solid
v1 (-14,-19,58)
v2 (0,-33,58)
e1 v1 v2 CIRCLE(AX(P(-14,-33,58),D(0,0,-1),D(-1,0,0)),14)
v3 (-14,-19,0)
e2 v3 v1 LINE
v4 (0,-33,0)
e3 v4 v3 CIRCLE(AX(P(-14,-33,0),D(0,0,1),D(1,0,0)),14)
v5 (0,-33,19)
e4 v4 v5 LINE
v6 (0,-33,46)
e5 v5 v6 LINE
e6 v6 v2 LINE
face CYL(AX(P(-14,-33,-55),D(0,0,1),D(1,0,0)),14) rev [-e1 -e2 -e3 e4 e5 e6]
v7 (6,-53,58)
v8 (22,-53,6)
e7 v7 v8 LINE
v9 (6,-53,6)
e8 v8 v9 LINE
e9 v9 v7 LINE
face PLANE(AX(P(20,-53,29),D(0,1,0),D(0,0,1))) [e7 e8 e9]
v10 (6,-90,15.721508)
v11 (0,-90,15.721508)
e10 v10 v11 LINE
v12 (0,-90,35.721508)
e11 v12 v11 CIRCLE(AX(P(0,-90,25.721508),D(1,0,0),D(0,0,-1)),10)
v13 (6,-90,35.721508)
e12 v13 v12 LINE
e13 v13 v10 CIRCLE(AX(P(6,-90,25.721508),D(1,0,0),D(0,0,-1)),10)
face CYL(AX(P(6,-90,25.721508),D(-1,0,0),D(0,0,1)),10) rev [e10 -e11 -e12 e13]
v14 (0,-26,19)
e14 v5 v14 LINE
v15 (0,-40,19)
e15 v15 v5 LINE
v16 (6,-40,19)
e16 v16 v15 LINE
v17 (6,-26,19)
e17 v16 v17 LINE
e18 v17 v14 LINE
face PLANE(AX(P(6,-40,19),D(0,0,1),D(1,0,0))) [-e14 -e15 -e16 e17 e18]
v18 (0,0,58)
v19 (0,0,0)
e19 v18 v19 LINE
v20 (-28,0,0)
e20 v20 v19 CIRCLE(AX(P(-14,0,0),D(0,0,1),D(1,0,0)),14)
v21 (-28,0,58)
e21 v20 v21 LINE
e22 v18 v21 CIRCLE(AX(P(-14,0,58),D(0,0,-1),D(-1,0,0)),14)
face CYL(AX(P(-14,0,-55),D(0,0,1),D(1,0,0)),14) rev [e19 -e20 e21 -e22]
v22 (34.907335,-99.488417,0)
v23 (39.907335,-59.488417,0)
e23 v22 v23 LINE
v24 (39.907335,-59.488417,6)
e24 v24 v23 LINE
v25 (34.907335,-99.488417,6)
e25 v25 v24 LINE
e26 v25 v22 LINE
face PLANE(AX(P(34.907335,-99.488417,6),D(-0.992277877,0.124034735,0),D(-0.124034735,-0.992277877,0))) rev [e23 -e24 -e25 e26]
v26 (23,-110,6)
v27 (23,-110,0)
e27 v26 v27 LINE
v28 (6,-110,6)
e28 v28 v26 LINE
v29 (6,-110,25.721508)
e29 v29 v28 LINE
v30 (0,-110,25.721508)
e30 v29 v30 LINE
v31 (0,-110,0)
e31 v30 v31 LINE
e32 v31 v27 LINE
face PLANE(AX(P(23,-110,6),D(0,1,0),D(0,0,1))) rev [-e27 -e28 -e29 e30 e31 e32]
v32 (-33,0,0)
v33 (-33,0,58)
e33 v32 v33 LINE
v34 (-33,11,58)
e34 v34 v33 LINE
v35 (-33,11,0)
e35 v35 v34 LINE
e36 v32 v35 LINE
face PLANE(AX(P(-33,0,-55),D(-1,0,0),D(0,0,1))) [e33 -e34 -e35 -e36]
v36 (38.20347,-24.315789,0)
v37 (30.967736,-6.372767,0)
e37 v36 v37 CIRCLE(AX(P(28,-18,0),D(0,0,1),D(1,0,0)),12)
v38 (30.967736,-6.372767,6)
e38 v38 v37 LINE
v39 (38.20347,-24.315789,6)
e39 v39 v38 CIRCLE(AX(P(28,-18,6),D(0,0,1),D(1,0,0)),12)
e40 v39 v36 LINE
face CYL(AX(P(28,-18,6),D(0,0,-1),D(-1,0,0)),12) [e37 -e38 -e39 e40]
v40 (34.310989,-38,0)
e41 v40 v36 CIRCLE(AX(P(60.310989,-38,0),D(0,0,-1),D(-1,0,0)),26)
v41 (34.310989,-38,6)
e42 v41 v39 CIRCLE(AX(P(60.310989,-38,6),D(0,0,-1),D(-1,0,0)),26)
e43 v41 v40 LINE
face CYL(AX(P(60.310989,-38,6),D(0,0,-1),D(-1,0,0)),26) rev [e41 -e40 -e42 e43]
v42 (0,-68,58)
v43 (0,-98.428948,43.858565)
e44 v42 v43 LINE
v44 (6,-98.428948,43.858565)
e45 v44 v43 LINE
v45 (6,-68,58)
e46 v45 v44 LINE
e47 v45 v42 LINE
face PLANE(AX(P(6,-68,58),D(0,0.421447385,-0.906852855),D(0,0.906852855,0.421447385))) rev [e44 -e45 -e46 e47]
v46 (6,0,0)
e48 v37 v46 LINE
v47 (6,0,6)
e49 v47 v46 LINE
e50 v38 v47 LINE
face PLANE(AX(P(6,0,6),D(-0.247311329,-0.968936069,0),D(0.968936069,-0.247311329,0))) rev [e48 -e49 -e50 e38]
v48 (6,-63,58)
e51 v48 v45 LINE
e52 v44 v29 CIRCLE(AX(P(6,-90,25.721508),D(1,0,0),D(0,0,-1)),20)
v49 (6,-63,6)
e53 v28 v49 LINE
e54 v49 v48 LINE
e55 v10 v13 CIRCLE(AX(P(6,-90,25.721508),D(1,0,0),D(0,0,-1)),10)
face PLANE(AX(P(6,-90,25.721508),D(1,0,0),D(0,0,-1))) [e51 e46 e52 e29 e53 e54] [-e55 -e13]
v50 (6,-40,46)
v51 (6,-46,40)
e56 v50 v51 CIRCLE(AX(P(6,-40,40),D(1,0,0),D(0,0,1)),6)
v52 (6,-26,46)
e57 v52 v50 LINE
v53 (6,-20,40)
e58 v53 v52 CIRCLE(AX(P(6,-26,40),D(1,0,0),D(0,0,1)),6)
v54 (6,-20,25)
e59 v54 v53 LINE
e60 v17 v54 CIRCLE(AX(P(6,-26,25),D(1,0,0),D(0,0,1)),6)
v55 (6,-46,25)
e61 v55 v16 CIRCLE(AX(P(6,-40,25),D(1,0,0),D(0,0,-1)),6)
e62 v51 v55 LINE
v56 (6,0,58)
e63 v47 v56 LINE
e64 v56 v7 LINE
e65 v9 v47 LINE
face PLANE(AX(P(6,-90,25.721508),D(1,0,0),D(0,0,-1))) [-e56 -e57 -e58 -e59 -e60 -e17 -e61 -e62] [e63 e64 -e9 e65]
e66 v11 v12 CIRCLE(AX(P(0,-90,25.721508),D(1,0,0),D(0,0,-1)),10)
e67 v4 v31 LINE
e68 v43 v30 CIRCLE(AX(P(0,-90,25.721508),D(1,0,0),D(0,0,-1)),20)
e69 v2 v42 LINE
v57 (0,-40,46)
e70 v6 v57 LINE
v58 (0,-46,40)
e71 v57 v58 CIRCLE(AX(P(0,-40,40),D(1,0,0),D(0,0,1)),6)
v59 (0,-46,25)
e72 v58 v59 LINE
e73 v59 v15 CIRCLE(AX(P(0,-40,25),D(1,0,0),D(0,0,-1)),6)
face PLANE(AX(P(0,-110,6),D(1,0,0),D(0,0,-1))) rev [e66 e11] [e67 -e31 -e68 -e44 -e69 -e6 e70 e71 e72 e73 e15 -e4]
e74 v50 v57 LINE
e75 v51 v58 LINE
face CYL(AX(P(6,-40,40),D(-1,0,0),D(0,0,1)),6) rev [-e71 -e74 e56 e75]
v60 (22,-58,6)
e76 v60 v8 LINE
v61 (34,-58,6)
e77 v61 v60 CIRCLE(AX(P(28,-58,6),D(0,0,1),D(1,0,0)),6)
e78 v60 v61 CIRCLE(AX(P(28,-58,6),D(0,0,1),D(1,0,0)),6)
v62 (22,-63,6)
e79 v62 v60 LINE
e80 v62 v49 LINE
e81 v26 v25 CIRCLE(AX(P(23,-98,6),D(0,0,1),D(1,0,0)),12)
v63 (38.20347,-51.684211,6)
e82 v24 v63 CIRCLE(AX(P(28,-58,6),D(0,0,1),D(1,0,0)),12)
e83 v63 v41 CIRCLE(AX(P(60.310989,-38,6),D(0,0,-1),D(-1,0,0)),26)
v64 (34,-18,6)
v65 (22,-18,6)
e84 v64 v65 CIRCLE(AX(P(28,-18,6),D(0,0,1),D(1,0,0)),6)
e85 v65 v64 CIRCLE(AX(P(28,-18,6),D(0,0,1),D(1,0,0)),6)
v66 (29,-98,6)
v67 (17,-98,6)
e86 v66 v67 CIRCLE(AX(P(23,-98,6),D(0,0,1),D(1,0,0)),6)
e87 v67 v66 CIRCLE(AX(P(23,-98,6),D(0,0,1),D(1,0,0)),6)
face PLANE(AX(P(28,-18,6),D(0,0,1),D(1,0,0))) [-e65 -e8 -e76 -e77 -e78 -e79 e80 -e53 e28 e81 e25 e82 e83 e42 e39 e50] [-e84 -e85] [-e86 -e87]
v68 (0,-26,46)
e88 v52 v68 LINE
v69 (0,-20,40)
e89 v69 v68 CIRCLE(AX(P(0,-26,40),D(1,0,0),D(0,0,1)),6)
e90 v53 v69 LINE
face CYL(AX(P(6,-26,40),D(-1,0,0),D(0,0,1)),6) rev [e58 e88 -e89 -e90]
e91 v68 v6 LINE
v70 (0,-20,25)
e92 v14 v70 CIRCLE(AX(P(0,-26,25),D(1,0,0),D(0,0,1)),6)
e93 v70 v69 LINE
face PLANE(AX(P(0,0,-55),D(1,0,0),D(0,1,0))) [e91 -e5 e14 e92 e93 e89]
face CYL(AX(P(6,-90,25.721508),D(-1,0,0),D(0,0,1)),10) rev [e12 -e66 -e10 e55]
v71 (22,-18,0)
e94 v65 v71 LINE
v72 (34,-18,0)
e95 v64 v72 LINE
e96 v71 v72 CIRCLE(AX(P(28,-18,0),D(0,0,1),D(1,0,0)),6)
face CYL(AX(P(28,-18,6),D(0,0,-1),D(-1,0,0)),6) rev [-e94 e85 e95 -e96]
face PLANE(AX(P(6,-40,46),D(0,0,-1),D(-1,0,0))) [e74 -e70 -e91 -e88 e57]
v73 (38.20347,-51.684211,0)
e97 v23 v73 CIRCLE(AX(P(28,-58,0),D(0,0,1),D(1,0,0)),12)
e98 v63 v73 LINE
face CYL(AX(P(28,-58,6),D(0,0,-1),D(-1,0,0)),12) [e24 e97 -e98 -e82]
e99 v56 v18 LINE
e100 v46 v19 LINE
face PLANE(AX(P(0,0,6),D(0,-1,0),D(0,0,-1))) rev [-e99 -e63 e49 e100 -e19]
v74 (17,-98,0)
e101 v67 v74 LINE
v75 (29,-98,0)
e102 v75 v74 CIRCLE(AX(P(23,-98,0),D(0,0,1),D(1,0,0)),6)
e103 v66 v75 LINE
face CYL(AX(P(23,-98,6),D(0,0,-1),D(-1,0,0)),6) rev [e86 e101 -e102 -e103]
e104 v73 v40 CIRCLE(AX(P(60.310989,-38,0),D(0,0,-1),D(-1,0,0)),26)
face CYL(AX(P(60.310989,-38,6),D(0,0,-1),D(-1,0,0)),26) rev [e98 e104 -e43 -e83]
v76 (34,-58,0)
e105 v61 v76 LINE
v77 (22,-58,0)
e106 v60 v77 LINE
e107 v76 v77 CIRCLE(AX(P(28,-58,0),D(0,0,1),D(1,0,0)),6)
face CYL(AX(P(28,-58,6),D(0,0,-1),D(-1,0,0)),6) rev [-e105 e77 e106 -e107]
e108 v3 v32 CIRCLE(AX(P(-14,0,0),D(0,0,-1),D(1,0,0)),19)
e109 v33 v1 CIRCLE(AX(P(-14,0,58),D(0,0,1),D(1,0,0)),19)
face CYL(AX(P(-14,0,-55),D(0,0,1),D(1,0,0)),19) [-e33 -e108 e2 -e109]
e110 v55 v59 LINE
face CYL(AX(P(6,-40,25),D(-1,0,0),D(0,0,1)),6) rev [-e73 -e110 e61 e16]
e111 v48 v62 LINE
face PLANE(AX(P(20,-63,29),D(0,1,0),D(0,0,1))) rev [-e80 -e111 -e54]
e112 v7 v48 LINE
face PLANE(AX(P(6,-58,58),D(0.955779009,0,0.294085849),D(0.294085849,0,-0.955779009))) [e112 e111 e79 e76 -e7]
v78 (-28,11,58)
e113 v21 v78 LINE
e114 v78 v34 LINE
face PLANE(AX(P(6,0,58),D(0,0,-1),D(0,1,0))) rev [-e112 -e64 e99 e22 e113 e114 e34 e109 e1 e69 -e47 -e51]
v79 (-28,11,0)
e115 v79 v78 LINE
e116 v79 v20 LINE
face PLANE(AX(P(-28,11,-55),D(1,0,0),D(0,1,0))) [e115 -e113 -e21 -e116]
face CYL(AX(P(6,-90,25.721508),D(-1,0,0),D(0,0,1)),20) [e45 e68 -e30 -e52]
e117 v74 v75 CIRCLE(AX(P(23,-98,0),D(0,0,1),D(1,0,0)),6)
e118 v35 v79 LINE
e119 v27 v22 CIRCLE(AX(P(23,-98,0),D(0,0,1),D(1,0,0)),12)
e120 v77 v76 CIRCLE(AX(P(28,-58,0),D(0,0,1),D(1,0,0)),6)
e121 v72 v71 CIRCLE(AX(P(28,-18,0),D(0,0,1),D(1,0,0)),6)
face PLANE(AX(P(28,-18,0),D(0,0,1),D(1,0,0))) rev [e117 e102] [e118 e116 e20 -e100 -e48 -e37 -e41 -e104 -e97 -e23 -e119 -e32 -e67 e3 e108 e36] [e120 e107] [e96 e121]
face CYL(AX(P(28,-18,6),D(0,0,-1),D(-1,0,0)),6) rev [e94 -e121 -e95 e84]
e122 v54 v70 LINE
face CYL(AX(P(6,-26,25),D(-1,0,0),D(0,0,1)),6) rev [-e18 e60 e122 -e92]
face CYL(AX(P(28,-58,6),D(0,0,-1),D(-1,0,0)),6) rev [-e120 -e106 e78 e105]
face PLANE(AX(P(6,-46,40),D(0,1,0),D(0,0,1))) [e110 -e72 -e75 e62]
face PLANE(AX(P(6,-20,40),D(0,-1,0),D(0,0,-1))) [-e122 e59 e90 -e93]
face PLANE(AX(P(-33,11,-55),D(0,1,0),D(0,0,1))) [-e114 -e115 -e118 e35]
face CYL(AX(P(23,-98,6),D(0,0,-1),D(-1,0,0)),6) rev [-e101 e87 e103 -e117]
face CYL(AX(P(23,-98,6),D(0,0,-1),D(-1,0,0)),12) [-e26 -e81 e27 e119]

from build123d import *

# Parameters (mm, degrees)
BACK_PLATE_PROFILE_R   = 6
BACK_PLATE_6MM_DEPTH   = 6
SIDE_FLANGE_PROFILE_R  = 10
SIDE_FLANGE_6MM_DEPTH  = 6
GUSSET_RIB_10MM_REACH  = 93.258
GUSSET_RIB_PATH_WALL_W = 238.92163478
GUSSET_RIB_PATH_WALL_H = 10
CRADLE_SADDLE_REACH    = 132.629


with BuildPart() as part:
    # Back Plate Profile → Back Plate 6mm (new body)
    with BuildSketch(Plane.XY):
        with BuildLine():
            Line((0, 0), (6, 0))
            Line((6, 0), (30.967735953, -6.372767169))
            ThreePointArc((30.967735953, -6.372767169), (39.129158997, -13.512036094), (38.203470161, -24.315789474))
            ThreePointArc((38.203470161, -24.315789474), (34.310988843, -38), (38.203470161, -51.684210526))
            ThreePointArc((38.203470161, -51.684210526), (39.723835971, -55.440376954), (39.907334521, -59.488416815))
            Line((39.907334521, -59.488416815), (34.907334521, -99.488416815))
            ThreePointArc((34.907334521, -99.488416815), (30.941630759, -106.99613811), (23, -110))
            Line((23, -110), (0, -110))
            Line((0, -110), (0, 0))
        make_face()
        with Locations((23, -98)):
            Circle(BACK_PLATE_PROFILE_R, mode=Mode.SUBTRACT)
        with Locations((28, -58)):
            Circle(BACK_PLATE_PROFILE_R, mode=Mode.SUBTRACT)
        with Locations((28, -18)):
            Circle(BACK_PLATE_PROFILE_R, mode=Mode.SUBTRACT)
    extrude(amount=BACK_PLATE_6MM_DEPTH)

    # Side Flange Profile → Side Flange 6mm (add)
    with BuildSketch(Plane(origin=(0, 0, 0), x_dir=(0, 0, -1), z_dir=(1, 0, 0))):
        with BuildLine():
            Line((0, 0), (-58, 0))
            Line((-58, 0), (-58, -68))
            Line((-58, -68), (-43.858565284, -98.428947708))
            ThreePointArc((-43.858565284, -98.428947708), (-36.478390759, -106.860886011), (-25.721508176, -110))
            Line((-25.721508176, -110), (-5.721508176, -110))
            Line((-5.721508176, -110), (0, -110))
            Line((0, -110), (0, 0))
        make_face()
        with Locations((-25.721508176, -90)):
            Circle(SIDE_FLANGE_PROFILE_R, mode=Mode.SUBTRACT)
        with BuildLine():
            Line((-40, -46), (-25, -46))
            ThreePointArc((-25, -46), (-20.757359313, -44.242640687), (-19, -40))
            Line((-19, -40), (-19, -26))
            ThreePointArc((-19, -26), (-20.757359313, -21.757359313), (-25, -20))
            Line((-25, -20), (-40, -20))
            ThreePointArc((-40, -20), (-44.242640687, -21.757359313), (-46, -26))
            Line((-46, -26), (-46, -40))
            ThreePointArc((-46, -40), (-44.242640687, -44.242640687), (-40, -46))
        make_face(mode=Mode.SUBTRACT)
    extrude(amount=SIDE_FLANGE_6MM_DEPTH)

    # Gusset Rib Path wall → Gusset Rib 10mm (add, up to next)
    with BuildSketch(Plane(origin=(14, -58, 32), x_dir=(0.294085848838, 0, -0.955779008722), z_dir=(-0.955779008722, 0, -0.294085848838)), mode=Mode.PRIVATE) as gusset_rib_10mm_sk1:
        Rectangle(GUSSET_RIB_PATH_WALL_W, GUSSET_RIB_PATH_WALL_H)
    gusset_rib_10mm_tool1 = extrude(gusset_rib_10mm_sk1.sketch, amount=GUSSET_RIB_10MM_REACH, mode=Mode.PRIVATE) - part.part
    add(gusset_rib_10mm_tool1.solids().sort_by_distance((14, -58, 32))[0])

    # Cradle Saddle: up to this face of the body (flat: up to its plane)
    cradle_saddle_end = Plane(part.part.faces().sort_by_distance((17.427592869, -55.606488982, 0))[0])
    # Cradle Saddle Profile → Cradle Saddle (add, up to the picked face)
    with BuildSketch(Plane.XY.offset(58), mode=Mode.PRIVATE) as cradle_saddle_sk1:
        with BuildLine():
            Line((-33, 0), (-33, 11))
            Line((-33, 11), (-28, 11))
            Line((-28, 11), (-28, 0))
            ThreePointArc((-28, 0), (-14, -14), (0, 0))
            Line((0, 0), (0, -33))
            ThreePointArc((0, -33), (-4.100505063, -23.100505063), (-14, -19))
            ThreePointArc((-14, -19), (-27.435028843, -13.435028843), (-33, 0))
        make_face()
    cradle_saddle_tool1 = split(extrude(cradle_saddle_sk1.sketch, amount=-CRADLE_SADDLE_REACH, mode=Mode.PRIVATE), bisect_by=cradle_saddle_end, keep=Keep.BOTH, mode=Mode.PRIVATE)
    add(cradle_saddle_tool1.solids().sort_by(Axis((-27.04612, -13.04612, 58), (0, 0, -1)))[0])


solid = part.part
